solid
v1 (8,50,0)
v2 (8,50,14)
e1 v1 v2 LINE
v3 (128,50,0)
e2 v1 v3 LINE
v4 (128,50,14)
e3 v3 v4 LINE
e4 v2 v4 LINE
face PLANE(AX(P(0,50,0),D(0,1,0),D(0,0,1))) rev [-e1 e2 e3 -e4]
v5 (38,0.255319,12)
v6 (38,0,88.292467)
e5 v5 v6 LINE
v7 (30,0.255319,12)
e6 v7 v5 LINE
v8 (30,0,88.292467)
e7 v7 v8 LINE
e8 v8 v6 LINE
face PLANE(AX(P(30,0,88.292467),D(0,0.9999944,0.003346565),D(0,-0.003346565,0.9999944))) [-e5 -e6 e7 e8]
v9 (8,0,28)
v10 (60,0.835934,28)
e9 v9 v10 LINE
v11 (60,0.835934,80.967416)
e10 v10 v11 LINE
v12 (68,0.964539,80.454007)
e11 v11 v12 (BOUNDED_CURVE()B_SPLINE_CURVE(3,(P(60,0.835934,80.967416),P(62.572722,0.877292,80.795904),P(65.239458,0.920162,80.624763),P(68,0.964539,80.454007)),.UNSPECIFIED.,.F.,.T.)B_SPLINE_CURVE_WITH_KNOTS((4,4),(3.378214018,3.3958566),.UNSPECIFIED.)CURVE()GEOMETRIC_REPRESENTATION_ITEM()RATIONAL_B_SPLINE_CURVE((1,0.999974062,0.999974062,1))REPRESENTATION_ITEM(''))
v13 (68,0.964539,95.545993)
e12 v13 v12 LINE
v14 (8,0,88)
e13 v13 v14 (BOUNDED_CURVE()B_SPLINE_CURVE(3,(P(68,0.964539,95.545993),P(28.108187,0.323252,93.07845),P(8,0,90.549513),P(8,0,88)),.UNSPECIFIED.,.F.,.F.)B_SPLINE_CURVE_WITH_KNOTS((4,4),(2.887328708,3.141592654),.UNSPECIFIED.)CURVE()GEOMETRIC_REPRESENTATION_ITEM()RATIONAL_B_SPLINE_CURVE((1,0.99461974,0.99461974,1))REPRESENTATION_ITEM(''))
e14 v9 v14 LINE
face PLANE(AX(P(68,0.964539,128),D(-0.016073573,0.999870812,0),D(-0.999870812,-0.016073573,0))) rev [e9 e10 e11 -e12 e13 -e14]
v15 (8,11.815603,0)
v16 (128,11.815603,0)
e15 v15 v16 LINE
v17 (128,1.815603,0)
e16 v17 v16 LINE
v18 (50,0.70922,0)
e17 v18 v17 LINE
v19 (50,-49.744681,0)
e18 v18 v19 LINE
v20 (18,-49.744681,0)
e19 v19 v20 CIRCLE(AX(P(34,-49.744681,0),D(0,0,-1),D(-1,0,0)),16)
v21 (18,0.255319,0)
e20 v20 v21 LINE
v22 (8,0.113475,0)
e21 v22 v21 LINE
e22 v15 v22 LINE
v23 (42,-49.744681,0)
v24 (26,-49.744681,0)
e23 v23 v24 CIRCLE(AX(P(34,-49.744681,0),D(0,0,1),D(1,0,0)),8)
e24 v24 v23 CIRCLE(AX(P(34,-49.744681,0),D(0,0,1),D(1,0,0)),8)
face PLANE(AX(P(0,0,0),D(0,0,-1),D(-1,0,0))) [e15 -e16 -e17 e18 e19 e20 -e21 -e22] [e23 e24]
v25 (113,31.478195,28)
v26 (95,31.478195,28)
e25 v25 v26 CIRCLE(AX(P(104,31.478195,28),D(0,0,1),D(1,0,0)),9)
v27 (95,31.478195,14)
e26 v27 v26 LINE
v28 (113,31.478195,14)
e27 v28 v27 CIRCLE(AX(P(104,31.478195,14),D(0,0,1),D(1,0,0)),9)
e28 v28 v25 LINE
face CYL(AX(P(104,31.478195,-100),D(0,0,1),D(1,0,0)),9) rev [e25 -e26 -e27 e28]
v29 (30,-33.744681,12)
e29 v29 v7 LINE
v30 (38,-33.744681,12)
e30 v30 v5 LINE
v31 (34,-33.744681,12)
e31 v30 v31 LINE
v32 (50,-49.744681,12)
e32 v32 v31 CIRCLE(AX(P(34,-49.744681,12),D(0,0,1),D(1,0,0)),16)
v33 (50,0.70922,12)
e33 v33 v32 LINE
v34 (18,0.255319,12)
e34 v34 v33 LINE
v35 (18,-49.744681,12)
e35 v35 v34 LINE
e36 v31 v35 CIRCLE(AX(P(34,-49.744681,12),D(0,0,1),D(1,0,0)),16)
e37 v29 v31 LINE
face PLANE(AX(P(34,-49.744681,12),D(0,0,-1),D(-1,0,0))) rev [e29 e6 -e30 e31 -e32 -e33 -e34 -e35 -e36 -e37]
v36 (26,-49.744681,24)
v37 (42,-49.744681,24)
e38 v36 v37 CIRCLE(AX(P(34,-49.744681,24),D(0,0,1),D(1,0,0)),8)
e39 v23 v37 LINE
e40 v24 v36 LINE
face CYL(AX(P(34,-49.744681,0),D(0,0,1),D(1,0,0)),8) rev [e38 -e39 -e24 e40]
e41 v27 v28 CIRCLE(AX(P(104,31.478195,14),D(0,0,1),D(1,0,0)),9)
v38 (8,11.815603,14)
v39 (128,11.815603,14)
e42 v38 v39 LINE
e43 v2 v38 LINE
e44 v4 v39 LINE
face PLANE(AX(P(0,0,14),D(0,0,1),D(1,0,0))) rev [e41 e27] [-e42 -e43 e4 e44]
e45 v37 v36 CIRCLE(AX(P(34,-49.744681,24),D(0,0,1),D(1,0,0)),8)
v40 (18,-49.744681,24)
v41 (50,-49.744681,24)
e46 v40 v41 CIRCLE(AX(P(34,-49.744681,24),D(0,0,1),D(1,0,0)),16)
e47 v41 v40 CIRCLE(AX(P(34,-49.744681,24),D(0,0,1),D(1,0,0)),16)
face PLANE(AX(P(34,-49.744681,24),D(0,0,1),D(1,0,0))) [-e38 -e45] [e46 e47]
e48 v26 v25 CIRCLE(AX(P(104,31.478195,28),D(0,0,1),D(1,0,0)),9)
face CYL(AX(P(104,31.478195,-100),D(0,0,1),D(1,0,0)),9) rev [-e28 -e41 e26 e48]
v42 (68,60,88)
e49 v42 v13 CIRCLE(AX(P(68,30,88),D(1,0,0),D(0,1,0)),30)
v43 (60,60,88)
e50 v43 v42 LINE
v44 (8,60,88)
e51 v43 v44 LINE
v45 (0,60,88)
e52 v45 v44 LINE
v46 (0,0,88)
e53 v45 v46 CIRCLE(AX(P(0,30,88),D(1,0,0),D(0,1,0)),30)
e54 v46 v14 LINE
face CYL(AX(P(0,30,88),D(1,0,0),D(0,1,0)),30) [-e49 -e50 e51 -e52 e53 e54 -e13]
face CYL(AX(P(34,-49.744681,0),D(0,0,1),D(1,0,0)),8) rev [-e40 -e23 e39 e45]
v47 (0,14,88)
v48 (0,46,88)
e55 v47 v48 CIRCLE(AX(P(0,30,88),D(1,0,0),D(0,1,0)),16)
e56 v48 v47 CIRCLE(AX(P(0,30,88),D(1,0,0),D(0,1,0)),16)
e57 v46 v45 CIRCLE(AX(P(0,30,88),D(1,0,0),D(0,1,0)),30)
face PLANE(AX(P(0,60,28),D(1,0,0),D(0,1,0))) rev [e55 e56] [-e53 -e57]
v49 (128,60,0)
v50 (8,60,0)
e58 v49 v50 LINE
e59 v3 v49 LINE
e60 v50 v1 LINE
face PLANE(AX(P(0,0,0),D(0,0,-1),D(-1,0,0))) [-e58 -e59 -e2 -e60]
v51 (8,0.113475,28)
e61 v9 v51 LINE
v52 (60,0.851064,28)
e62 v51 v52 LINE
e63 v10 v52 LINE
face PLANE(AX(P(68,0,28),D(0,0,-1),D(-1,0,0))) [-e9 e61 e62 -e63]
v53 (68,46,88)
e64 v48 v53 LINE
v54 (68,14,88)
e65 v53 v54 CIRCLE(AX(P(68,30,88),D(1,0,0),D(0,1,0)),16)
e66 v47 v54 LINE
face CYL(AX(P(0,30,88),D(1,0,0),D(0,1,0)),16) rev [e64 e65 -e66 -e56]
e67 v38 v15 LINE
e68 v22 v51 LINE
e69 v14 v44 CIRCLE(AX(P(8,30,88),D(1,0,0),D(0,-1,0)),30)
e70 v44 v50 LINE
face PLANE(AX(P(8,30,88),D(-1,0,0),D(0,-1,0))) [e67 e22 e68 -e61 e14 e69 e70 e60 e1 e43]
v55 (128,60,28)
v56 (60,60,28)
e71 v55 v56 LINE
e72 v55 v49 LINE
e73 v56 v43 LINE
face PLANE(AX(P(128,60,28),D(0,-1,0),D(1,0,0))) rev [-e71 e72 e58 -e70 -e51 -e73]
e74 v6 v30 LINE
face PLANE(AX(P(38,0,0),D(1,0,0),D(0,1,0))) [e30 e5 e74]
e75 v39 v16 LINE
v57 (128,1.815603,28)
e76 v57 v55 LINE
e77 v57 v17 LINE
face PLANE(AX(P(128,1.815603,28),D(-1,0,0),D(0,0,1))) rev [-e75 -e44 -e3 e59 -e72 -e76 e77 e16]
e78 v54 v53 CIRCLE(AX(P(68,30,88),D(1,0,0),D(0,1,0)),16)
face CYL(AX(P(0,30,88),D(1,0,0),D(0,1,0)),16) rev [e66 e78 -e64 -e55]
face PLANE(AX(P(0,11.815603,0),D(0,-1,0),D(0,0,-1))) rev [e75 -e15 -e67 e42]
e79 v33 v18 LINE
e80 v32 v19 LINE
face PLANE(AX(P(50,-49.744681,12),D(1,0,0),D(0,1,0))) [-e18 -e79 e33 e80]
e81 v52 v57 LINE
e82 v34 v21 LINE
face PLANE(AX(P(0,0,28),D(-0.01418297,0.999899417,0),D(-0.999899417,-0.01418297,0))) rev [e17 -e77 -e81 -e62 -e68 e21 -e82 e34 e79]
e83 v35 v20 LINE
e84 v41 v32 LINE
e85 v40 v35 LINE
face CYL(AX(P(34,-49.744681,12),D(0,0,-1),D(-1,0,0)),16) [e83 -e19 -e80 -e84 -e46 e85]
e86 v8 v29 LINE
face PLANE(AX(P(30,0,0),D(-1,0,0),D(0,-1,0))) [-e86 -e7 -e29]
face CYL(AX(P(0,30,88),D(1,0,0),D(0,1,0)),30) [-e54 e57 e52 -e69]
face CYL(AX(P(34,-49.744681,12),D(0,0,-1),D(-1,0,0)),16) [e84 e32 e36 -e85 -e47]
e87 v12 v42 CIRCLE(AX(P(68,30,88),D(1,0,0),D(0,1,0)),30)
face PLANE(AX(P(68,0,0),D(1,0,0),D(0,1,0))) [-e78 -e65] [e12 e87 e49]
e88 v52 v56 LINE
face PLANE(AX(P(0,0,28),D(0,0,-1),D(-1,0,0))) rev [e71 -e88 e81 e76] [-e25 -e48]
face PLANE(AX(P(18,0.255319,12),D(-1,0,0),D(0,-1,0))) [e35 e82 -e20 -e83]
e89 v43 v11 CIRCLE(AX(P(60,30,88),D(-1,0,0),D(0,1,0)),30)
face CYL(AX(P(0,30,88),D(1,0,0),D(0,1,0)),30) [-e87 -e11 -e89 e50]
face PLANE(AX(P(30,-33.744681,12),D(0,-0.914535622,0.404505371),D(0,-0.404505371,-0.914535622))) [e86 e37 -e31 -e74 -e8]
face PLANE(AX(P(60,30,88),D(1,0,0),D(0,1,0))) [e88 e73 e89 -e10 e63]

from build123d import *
from build123d.topology import SkipClean

# Parameters (mm, degrees)
BASE_BLOCK_DEPTH            = 28
UPRIGHT_WALL_SKETCH_W       = 60
UPRIGHT_WALL_SKETCH_H       = 60
UPRIGHT_WALL_DEPTH          = 68
BEARING_BOSS_SKETCH_R       = 30
BEARING_BOSS_60_DEPTH       = 68
BEARING_BORE_SKETCH_R       = 16
BEARING_BORE_32_DEPTH       = 68
BASE_PROFILE_CUT_DEPTH      = 128
THROUGH_HOLE_SKETCH_R       = 9
THROUGH_HOLE_18_DEPTH       = 128
END_START                   = -8
END_CHANNEL_RECESS_DEPTH    = 8
WALL_RECESS_DEPTH           = 8
TRIANGULAR_RELIEF_CUT_DEPTH = 100
SIDE_LUG_PLATE_DEPTH        = 12
LUG_BOSS_SKETCH_R           = 16
LUG_BOSS_32_DEPTH           = 12
LUG_GUSSET_DEPTH            = 20
GUSSET_TRIM_CUT_DEPTH       = 12
LUG_HOLE_SKETCH_R           = 8
LUG_HOLE_16_DEPTH           = 24


with BuildPart() as part:
    # Base Block Sketch → Base Block (new body)
    with BuildSketch(Plane.XY):
        Polygon((0, 0), (128, 1.815602837), (128, 60), (0, 60), align=None)
    extrude(amount=BASE_BLOCK_DEPTH)

    # Upright Wall Sketch → Upright Wall (add)
    with BuildSketch(Plane.ZY):
        with Locations((58, 30)):
            Rectangle(UPRIGHT_WALL_SKETCH_W, UPRIGHT_WALL_SKETCH_H)
    extrude(amount=-UPRIGHT_WALL_DEPTH)

    # Bearing Boss Sketch → Bearing Boss Ø60 (add)
    with BuildSketch(Plane(origin=(68, 0, 0), x_dir=(0, 0, -1), z_dir=(1, 0, 0))):
        with Locations((-88, 30)):
            Circle(BEARING_BOSS_SKETCH_R)
    extrude(amount=-BEARING_BOSS_60_DEPTH)

    # Bearing Bore Sketch → Bearing Bore Ø32 (cut)
    with BuildSketch(Plane(origin=(68, 0, 0), x_dir=(0, 0, -1), z_dir=(1, 0, 0))):
        with Locations(Location((-88, 30, 0), (0, 0, 90))):
            Circle(BEARING_BORE_SKETCH_R)
    extrude(amount=-BEARING_BORE_32_DEPTH, mode=Mode.SUBTRACT)

    # Base Profile Cut Sketch → Base Profile Cut (cut)
    with BuildSketch(Plane(origin=(128, 0, 0), x_dir=(0, 0, -1), z_dir=(1, 0, 0))):
        Polygon((0, 11.815602837), (0, 50), (-14, 50), (-14, 30.907801418), (-14, 11.815602837), align=None)
    extrude(amount=-BASE_PROFILE_CUT_DEPTH, mode=Mode.SUBTRACT)

    # Through Hole Sketch → Through Hole Ø18 (cut)
    with BuildSketch(Plane.XY.offset(28)):
        with Locations((104, 31.47819511)):
            Circle(THROUGH_HOLE_SKETCH_R)
    extrude(amount=-THROUGH_HOLE_18_DEPTH, mode=Mode.SUBTRACT)

    # End Channel Recess Sketch → End Channel Recess (cut)
    with SkipClean():  # the faces are left unmerged after this step: merging them gives an invalid solid
        with BuildSketch(Plane.ZY.offset(END_START)):
            with BuildLine():
                Line((0, 60), (88, 60))
                ThreePointArc((88, 60), (58, 30), (88, 0))
                Line((88, 0), (0, 0))
                Line((0, 0), (0, 11.815602837))
                Line((0, 11.815602837), (14, 11.815602837))
                Line((14, 11.815602837), (14, 50))
                Line((14, 50), (0, 50))
                Line((0, 50), (0, 60))
            make_face()
        extrude(amount=END_CHANNEL_RECESS_DEPTH, mode=Mode.SUBTRACT)

    # Wall Recess Sketch → Wall Recess (cut)
    with SkipClean():  # the faces are left unmerged after this step: merging them gives an invalid solid
        with BuildSketch(Plane(origin=(68, 0, 0), x_dir=(0, 0, -1), z_dir=(1, 0, 0))):
            with BuildLine():
                Line((-28, 60), (-28, 0))
                Line((-28, 0), (-88, 0))
                ThreePointArc((-88, 0), (-58, 30), (-88, 60))
                Line((-88, 60), (-28, 60))
            make_face()
        extrude(amount=-WALL_RECESS_DEPTH, mode=Mode.SUBTRACT)

    # Triangular Relief Sketch → Triangular Relief Cut (cut)
    with SkipClean():  # the faces are left unmerged after this step: merging them gives an invalid solid
        with BuildSketch(Plane(origin=(0, 0, 28), x_dir=(-1, 0, 0), z_dir=(0, 0, -1))):
            Polygon((-68, 0), (-68, 0.964539007), (-8, 0), align=None)
        extrude(amount=-TRIANGULAR_RELIEF_CUT_DEPTH, mode=Mode.SUBTRACT)

    # Side Lug Plate Sketch → Side Lug Plate (add)
    with SkipClean():  # the faces are left unmerged after this step: merging them gives an invalid solid
        with BuildSketch(Plane(origin=(0, 0, 0), x_dir=(-1, 0, 0), z_dir=(0, 0, -1))):
            with BuildLine():
                Line((-50, -49.744680851), (-50, 0.709219858))
                Line((-50, 0.709219858), (-18, 0.255319149))
                Line((-18, 0.255319149), (-18, -49.744680851))
                ThreePointArc((-18, -49.744680851), (-34, -65.744680851), (-50, -49.744680851))
            make_face()
        extrude(amount=-SIDE_LUG_PLATE_DEPTH)

    # Lug Boss Sketch → Lug Boss Ø32 (add)
    with SkipClean():  # the faces are left unmerged after this step: merging them gives an invalid solid
        with BuildSketch(Plane.XY.offset(12)):
            with Locations((34, -49.744680851)):
                Circle(LUG_BOSS_SKETCH_R)
        extrude(amount=LUG_BOSS_32_DEPTH)

    # Lug Gusset Sketch → Lug Gusset (add)
    with SkipClean():  # the faces are left unmerged after this step: merging them gives an invalid solid
        with BuildSketch(Plane(origin=(50, 0, 0), x_dir=(0, 0, -1), z_dir=(1, 0, 0))):
            Polygon((-12, 0.255319149), (-12, -33.744680851), (-88.292467077, 0), align=None)
        extrude(amount=-LUG_GUSSET_DEPTH)

    # Gusset Trim Sketch → Gusset Trim Cut (cut)
    with SkipClean():  # the faces are left unmerged after this step: merging them gives an invalid solid
        with BuildSketch(Plane(origin=(50, 0, 0), x_dir=(0, 0, -1), z_dir=(1, 0, 0))):
            Polygon((-88.292467077, 0), (-12, 0.255319149), (-12, -33.744680851), align=None)
        extrude(amount=-GUSSET_TRIM_CUT_DEPTH, mode=Mode.SUBTRACT)

    # Lug Hole Sketch → Lug Hole Ø16 (cut)
    with SkipClean():  # the faces are left unmerged after this step: merging them gives an invalid solid
        with BuildSketch(Plane.XY.offset(24)):
            with Locations((34, -49.744680851)):
                Circle(LUG_HOLE_SKETCH_R)
        extrude(amount=-LUG_HOLE_16_DEPTH, mode=Mode.SUBTRACT)


solid = part.part
